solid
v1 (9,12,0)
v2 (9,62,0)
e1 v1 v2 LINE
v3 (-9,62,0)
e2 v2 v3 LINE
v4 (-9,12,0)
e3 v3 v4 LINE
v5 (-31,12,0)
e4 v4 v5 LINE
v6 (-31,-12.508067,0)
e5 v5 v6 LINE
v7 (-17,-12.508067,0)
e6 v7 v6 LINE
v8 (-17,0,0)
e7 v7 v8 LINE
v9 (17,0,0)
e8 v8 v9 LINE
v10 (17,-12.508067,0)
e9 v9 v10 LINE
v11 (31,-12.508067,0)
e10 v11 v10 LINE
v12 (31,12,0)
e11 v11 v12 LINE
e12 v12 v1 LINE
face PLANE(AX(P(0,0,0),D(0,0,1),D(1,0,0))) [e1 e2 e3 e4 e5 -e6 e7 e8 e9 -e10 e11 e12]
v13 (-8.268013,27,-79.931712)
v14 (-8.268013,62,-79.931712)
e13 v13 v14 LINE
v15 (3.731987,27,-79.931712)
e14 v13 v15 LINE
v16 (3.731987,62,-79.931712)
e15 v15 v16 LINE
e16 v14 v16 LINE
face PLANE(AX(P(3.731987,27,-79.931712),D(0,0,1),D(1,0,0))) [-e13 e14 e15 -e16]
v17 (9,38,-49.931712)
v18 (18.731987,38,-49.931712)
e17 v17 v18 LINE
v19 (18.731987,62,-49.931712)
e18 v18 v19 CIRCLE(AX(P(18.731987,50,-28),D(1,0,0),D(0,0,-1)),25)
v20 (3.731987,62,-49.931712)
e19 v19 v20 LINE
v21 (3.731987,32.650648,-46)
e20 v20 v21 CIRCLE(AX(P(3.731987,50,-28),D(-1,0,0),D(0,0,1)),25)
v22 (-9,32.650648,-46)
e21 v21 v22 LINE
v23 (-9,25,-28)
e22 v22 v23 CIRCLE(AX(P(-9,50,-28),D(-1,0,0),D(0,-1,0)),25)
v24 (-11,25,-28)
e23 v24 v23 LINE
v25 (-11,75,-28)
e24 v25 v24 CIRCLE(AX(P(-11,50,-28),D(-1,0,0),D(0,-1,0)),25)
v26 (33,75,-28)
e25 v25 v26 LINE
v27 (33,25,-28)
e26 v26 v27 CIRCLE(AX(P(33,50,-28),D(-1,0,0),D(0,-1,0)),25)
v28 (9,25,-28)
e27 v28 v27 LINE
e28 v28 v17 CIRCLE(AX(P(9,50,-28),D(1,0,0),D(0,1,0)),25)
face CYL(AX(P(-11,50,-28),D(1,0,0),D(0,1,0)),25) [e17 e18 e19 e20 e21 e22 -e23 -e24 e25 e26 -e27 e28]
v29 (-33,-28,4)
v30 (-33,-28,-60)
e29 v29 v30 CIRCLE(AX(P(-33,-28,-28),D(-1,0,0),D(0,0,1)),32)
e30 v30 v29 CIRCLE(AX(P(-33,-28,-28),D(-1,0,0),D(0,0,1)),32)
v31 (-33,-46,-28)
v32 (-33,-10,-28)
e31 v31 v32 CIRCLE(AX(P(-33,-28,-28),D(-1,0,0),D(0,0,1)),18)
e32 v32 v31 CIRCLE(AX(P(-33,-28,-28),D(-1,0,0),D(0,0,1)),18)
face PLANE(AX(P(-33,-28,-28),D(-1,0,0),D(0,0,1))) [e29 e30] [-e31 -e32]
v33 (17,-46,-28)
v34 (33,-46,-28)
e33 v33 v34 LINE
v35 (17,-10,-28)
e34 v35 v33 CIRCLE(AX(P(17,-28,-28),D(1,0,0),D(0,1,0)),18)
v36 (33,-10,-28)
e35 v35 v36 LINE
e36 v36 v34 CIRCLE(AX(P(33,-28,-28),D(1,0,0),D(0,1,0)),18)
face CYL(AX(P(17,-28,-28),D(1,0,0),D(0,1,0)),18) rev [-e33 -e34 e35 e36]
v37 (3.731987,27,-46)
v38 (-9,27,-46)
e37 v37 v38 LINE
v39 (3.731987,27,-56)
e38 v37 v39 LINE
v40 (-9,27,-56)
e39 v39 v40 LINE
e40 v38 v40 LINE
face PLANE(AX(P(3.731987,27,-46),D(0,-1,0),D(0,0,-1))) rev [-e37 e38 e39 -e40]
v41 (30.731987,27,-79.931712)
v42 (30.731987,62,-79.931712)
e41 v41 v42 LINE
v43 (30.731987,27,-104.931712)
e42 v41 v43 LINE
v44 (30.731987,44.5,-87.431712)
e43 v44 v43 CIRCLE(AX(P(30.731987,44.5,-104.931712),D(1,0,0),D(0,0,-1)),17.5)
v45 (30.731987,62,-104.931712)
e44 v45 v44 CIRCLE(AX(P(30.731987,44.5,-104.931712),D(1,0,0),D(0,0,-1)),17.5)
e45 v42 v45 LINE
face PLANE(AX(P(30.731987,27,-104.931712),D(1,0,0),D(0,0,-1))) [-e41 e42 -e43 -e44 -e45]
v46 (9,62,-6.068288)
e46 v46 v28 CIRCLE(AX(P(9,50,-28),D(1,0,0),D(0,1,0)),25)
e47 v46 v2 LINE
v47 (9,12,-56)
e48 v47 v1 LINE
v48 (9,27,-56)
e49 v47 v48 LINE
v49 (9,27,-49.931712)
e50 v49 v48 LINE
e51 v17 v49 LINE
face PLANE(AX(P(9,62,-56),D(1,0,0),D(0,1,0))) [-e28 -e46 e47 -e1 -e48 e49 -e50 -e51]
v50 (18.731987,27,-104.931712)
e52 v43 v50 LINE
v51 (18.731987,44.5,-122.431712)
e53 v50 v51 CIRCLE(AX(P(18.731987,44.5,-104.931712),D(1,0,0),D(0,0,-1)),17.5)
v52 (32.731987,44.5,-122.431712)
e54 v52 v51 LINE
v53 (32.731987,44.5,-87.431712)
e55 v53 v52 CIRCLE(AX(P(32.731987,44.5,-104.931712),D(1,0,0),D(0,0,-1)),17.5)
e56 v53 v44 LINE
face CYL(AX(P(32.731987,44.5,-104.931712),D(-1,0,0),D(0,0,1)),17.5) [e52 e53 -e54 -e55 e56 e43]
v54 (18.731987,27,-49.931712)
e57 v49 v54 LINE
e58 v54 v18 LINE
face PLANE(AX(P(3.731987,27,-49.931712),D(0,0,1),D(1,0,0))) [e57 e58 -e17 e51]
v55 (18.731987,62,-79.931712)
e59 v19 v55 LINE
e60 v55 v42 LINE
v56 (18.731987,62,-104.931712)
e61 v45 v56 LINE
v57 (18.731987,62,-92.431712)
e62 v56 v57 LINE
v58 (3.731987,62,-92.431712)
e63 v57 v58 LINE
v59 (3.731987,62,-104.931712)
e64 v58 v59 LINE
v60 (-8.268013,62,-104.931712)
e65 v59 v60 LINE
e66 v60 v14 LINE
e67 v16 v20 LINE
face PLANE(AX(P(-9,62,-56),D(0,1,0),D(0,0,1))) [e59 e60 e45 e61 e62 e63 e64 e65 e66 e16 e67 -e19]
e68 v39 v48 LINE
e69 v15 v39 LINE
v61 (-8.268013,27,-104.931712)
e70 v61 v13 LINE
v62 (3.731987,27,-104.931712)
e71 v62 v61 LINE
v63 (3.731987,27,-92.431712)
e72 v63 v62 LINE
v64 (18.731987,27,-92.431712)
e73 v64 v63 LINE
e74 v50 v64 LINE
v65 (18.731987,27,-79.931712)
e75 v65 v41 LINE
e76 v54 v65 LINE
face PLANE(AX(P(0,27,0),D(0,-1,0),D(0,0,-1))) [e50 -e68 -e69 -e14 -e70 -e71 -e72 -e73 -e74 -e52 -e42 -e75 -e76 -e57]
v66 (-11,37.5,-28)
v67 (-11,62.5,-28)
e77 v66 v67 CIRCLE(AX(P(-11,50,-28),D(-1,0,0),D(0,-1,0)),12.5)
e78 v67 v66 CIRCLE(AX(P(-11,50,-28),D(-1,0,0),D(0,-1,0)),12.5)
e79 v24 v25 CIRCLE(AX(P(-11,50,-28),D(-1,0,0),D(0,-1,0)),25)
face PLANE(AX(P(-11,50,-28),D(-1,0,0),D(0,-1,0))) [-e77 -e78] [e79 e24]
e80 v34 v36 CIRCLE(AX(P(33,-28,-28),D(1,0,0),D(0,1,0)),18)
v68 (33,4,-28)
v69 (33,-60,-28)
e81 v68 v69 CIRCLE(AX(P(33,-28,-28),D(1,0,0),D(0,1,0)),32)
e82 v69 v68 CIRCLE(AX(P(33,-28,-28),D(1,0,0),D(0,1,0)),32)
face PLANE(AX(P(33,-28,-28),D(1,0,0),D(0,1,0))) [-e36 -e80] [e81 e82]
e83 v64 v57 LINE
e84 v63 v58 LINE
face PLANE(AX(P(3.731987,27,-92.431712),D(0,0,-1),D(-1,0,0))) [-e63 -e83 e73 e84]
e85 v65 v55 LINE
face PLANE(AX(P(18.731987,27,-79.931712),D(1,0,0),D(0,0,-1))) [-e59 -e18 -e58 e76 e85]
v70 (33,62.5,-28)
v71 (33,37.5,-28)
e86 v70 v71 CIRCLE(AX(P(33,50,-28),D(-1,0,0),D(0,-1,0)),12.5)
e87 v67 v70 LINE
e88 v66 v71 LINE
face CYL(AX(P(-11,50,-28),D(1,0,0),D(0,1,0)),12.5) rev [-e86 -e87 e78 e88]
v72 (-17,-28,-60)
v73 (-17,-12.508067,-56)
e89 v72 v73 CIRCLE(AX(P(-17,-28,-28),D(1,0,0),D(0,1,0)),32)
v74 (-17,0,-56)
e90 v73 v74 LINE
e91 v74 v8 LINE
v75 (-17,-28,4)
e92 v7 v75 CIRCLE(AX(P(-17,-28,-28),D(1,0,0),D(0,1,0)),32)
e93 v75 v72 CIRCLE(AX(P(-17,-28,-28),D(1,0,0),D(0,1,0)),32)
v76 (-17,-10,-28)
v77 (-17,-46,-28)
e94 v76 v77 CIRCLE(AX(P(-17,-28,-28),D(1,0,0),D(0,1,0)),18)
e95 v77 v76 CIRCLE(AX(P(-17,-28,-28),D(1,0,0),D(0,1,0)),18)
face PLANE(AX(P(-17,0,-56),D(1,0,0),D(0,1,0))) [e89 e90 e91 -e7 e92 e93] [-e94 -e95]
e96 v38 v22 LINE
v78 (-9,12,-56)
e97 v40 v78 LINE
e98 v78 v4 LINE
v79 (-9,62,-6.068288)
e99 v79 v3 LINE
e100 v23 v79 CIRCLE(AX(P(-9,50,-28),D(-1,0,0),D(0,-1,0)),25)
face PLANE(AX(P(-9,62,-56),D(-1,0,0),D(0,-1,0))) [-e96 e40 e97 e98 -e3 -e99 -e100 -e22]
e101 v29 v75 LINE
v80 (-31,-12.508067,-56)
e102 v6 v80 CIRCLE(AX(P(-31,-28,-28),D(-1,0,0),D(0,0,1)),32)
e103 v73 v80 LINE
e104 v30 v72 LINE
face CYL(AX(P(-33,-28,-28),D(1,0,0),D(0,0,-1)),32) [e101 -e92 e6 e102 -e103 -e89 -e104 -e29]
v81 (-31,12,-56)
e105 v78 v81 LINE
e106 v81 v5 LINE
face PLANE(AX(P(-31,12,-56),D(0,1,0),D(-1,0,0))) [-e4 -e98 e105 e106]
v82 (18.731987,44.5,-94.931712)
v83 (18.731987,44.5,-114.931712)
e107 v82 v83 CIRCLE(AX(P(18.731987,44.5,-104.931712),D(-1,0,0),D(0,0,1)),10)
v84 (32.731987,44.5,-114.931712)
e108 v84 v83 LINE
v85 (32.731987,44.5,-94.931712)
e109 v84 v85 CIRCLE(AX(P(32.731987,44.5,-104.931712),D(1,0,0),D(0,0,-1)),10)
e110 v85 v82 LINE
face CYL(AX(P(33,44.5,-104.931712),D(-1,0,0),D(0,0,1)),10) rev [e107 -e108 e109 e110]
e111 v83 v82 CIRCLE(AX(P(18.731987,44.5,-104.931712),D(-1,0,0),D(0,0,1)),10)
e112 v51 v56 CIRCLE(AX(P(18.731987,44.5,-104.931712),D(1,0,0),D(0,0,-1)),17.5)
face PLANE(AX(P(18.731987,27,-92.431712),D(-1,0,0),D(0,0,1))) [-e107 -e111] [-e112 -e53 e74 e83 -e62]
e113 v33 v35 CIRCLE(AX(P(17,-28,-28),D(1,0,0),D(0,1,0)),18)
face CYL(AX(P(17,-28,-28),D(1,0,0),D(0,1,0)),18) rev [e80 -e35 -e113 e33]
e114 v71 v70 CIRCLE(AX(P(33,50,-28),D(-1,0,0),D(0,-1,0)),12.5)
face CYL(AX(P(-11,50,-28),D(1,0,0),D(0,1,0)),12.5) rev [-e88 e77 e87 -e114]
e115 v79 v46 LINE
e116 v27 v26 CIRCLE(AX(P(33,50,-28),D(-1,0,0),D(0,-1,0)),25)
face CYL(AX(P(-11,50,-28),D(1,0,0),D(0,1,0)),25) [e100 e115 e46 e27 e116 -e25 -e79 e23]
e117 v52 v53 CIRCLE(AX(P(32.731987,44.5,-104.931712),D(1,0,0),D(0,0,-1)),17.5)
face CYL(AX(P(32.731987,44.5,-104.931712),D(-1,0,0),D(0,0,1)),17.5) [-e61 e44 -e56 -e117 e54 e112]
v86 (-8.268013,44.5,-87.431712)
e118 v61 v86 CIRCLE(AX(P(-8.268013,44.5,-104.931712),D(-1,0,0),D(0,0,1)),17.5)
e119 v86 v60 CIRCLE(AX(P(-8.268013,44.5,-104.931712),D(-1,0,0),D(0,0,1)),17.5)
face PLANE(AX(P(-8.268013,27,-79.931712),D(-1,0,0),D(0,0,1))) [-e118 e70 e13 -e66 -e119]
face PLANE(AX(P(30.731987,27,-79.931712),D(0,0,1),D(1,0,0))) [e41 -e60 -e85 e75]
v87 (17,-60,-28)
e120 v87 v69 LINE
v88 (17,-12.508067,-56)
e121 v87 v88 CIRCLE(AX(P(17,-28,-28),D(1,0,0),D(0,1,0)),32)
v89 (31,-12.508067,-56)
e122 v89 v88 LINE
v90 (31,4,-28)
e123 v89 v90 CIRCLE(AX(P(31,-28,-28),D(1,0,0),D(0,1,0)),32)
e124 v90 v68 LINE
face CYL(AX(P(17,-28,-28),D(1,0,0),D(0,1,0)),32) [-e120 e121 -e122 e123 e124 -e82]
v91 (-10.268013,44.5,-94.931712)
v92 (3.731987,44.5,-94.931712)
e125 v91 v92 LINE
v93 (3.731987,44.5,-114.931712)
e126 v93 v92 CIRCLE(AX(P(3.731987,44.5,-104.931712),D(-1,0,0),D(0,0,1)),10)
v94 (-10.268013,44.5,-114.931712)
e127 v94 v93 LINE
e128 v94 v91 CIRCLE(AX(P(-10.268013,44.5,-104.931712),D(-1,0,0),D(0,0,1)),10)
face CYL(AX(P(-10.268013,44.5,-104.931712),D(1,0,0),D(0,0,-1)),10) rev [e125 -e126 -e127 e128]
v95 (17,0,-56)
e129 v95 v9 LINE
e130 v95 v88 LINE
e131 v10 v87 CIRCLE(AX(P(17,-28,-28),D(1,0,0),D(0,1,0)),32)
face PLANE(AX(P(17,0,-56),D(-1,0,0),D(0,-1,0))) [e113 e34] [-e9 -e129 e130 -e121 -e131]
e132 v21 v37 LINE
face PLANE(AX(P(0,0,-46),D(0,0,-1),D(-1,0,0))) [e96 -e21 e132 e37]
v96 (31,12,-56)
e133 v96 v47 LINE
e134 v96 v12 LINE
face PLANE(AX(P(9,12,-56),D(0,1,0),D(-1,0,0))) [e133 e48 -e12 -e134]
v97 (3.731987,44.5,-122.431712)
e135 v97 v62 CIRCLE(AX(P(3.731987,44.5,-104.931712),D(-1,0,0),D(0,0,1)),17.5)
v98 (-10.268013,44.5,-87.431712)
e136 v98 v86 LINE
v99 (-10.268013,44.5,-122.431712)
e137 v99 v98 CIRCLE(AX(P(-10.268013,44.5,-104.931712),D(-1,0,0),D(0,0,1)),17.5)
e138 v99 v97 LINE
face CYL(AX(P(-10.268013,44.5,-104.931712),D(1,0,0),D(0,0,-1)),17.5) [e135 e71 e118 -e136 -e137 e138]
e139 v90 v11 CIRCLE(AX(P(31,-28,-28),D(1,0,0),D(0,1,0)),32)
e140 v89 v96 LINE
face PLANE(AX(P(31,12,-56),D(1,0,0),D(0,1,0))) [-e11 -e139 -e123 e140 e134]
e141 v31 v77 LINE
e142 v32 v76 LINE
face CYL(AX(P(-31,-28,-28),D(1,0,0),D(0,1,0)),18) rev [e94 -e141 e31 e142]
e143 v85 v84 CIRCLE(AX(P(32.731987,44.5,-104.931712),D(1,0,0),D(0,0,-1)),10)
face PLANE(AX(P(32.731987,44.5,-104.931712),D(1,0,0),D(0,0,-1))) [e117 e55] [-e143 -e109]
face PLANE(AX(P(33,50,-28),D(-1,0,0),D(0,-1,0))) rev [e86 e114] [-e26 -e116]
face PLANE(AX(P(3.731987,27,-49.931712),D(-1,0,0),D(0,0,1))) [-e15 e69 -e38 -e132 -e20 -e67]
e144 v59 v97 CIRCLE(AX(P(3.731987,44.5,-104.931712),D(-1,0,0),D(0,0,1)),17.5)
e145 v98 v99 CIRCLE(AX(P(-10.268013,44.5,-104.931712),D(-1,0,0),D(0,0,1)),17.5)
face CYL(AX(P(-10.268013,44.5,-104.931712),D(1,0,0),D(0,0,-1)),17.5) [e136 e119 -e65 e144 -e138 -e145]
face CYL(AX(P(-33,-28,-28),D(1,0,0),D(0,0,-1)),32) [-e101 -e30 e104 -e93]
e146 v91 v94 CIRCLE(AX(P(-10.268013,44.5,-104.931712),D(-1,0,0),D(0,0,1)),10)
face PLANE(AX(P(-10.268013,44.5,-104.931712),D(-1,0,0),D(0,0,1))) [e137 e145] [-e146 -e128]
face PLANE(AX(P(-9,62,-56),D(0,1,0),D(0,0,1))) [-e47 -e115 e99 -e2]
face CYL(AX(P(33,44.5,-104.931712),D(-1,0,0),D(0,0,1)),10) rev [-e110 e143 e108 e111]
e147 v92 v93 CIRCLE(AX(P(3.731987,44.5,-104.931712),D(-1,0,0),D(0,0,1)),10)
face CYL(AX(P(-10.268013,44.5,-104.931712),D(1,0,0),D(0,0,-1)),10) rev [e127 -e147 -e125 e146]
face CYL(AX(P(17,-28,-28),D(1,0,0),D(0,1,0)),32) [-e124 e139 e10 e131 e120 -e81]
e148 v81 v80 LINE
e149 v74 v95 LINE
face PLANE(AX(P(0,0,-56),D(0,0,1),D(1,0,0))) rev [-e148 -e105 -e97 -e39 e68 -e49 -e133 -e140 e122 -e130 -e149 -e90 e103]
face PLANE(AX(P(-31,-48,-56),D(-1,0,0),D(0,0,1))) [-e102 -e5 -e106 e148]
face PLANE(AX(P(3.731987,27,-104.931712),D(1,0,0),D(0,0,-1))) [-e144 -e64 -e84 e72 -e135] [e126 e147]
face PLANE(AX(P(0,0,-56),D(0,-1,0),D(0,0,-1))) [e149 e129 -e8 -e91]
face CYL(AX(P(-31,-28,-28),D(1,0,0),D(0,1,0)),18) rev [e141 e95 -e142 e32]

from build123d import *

# Parameters (mm, degrees)
BRACKET_BODY_DEPTH      = 56
SLOT_SKETCH_W           = 62
SLOT_SKETCH_H           = 20
SLOT_CUT_DEPTH          = 90.112288715
LUG_A_SKETCH_R          = 32
LUG_A_SKETCH_R_2        = 18
LUG_A_14MM_DEPTH        = 14
SPACER_START            = 2
SPACER_A_SKETCH_R       = 32
SPACER_A_SKETCH_R_2     = 18
SPACER_A_2MM_DEPTH      = 2
HOLE_A_SKETCH_R         = 18
HOLE_A_DEPTH            = 107.244999882
SPACER_B_SKETCH_R       = 32
SPACER_B_SKETCH_R_2     = 18
SPACER_B_2MM_DEPTH      = 2
LUG_B_SKETCH_R          = 32
LUG_B_SKETCH_R_2        = 18
LUG_B_14MM_DEPTH        = 14
PAD_SKETCH_R            = 25
PAD_SKETCH_R_2          = 12.5
PAD_2MM_DEPTH           = 2
HUB_START               = -44
HUB_SKETCH_R            = 25
HUB_SKETCH_R_2          = 12.5
HUB_44MM_DEPTH          = 44
HUB_BORE_SKETCH_R       = 12.5
HUB_BORE_DEPTH          = 44
ARM_35MM_DEPTH          = 35
ARM_SPACER_A_SKETCH_R   = 17.5
ARM_SPACER_A_SKETCH_R_2 = 10
ARM_SPACER_A_2MM_DEPTH  = 2
ARM_START               = -12
ARM_LUG_SKETCH_R        = 17.5
ARM_LUG_SKETCH_R_2      = 10
ARM_LUG_12MM_DEPTH      = 12
ARM_HOLE_SKETCH_R       = 10
ARM_HOLE_DEPTH          = 150.390672563
ARM_SPACER_B_SKETCH_R   = 17.5
ARM_SPACER_B_SKETCH_R_2 = 10
ARM_SPACER_B_2MM_DEPTH  = 2
ARM_START_2             = -14
ARM_EYE_SKETCH_R        = 17.5
ARM_EYE_SKETCH_R_2      = 10
ARM_EYE_14MM_DEPTH      = 14
ARM_SLOT_SKETCH_W       = 12.731987003
ARM_SLOT_SKETCH_H       = 35
ARM_SLOT_10MM_DEPTH     = 10
PIN_START               = -16
PIN_BOSS_SKETCH_R       = 25
PIN_BOSS_16MM_DEPTH     = 16
PIN_BOSS_HOLE_SKETCH_R  = 12.5
PIN_BOSS_HOLE_DEPTH     = 151.168319402


with BuildPart() as part:
    # Bracket Profile Sketch → Bracket Body (new body)
    with BuildSketch(Plane.XY):
        Polygon((0, 0), (17, 0), (17, -48), (31, -48), (31, 12), (9, 12), (9, 62), (-9, 62), (-9, 12), (-31, 12), (-31, -48), (-17, -48), (-17, 0), align=None)
    extrude(amount=-BRACKET_BODY_DEPTH)

    # Slot Sketch → Slot Cut (cut, through all)
    with BuildSketch(Plane.XY):
        with Locations((0, -38)):
            Rectangle(SLOT_SKETCH_W, SLOT_SKETCH_H)
    extrude(amount=-SLOT_CUT_DEPTH, mode=Mode.SUBTRACT)

    # Lug A Sketch → Lug A 14mm (add)
    with BuildSketch(Plane(origin=(31, 0, 0), x_dir=(0, 0, -1), z_dir=(1, 0, 0))):
        with Locations((28, -28)):
            Circle(LUG_A_SKETCH_R)
        with Locations((28, -28)):
            Circle(LUG_A_SKETCH_R_2, mode=Mode.SUBTRACT)
    extrude(amount=-LUG_A_14MM_DEPTH)

    # Spacer A Sketch → Spacer A 2mm (add)
    with BuildSketch(Plane(origin=(31, 0, 0), x_dir=(0, 0, -1), z_dir=(1, 0, 0)).offset(SPACER_START)):
        with Locations(Location((28, -28, 0), (0, 0, 90))):
            Circle(SPACER_A_SKETCH_R)
        with Locations(Location((28, -28, 0), (0, 0, 90))):
            Circle(SPACER_A_SKETCH_R_2, mode=Mode.SUBTRACT)
    extrude(amount=-SPACER_A_2MM_DEPTH)

    # Hole A Sketch → Hole A (cut, through all)
    with BuildSketch(Plane(origin=(31, 0, 0), x_dir=(0, 0, -1), z_dir=(1, 0, 0))):
        with Locations(Location((28, -28, 0), (0, 0, 90))):
            Circle(HOLE_A_SKETCH_R)
    extrude(amount=-HOLE_A_DEPTH, mode=Mode.SUBTRACT)

    # Spacer B Sketch → Spacer B 2mm (add)
    with BuildSketch(Plane.ZY.offset(31)):
        with Locations(Location((-28, -28, 0), (0, 0, 90))):
            Circle(SPACER_B_SKETCH_R)
        with Locations(Location((-28, -28, 0), (0, 0, 90))):
            Circle(SPACER_B_SKETCH_R_2, mode=Mode.SUBTRACT)
    extrude(amount=SPACER_B_2MM_DEPTH)

    # Lug B Sketch → Lug B 14mm (add)
    with BuildSketch(Plane(origin=(-17, 0, 0), x_dir=(0, 0, -1), z_dir=(1, 0, 0))):
        with Locations(Location((28, -28, 0), (0, 0, 90))):
            Circle(LUG_B_SKETCH_R)
        with Locations(Location((28, -28, 0), (0, 0, 90))):
            Circle(LUG_B_SKETCH_R_2, mode=Mode.SUBTRACT)
    extrude(amount=-LUG_B_14MM_DEPTH)

    # Pad Sketch → Pad 2mm (add)
    with BuildSketch(Plane.ZY.offset(9)):
        with Locations(Location((-28, 50, 0), (0, 0, 151.314597986))):
            Circle(PAD_SKETCH_R)
        with Locations(Location((-28, 50, 0), (0, 0, 73.739795292))):
            Circle(PAD_SKETCH_R_2, mode=Mode.SUBTRACT)
    extrude(amount=PAD_2MM_DEPTH)

    # Hub Sketch → Hub 44mm (add)
    with BuildSketch(Plane.ZY.offset(11).offset(HUB_START)):
        with Locations(Location((-28, 50, 0), (0, 0, 270))):
            Circle(HUB_SKETCH_R)
        with Locations(Location((-28, 50, 0), (0, 0, 270))):
            Circle(HUB_SKETCH_R_2, mode=Mode.SUBTRACT)
    extrude(amount=HUB_44MM_DEPTH)

    # Hub Bore Sketch → Hub Bore (cut)
    with BuildSketch(Plane.ZY.offset(9).offset(HUB_START)):
        with Locations(Location((-28, 50, 0), (0, 0, 270))):
            Circle(HUB_BORE_SKETCH_R)
    extrude(amount=HUB_BORE_DEPTH, mode=Mode.SUBTRACT)

    # Arm Profile Sketch → Arm 35mm (add)
    with BuildSketch(Plane(origin=(0, 62, 0), x_dir=(1, 0, 0), z_dir=(0, 1, 0))):
        Polygon((3.731987003, 49.931712199), (3.731987003, 79.931712199), (-8.268012997, 79.931712199), (-8.268012997, 104.931712199), (3.731987003, 104.931712199), (3.731987003, 92.431712199), (18.731987003, 92.431712199), (18.731987003, 104.931712199), (30.731987003, 104.931712199), (30.731987003, 79.931712199), (18.731987003, 79.931712199), (18.731987003, 49.931712199), align=None)
    extrude(amount=-ARM_35MM_DEPTH)

    # Arm Spacer A Sketch → Arm Spacer A 2mm (add)
    with BuildSketch(Plane.ZY.offset(8.268012997)):
        with Locations(Location((-104.931712199, 44.5, 0), (0, 0, 270))):
            Circle(ARM_SPACER_A_SKETCH_R)
        with Locations(Location((-104.931712199, 44.5, 0), (0, 0, 90))):
            Circle(ARM_SPACER_A_SKETCH_R_2, mode=Mode.SUBTRACT)
    extrude(amount=ARM_SPACER_A_2MM_DEPTH)

    # Arm Lug Sketch → Arm Lug 12mm (add)
    with BuildSketch(Plane.ZY.offset(8.268012997).offset(ARM_START)):
        with Locations(Location((-104.931712199, 44.5, 0), (0, 0, 90))):
            Circle(ARM_LUG_SKETCH_R)
        with Locations(Location((-104.931712199, 44.5, 0), (0, 0, 90))):
            Circle(ARM_LUG_SKETCH_R_2, mode=Mode.SUBTRACT)
    extrude(amount=ARM_LUG_12MM_DEPTH)

    # Arm Hole Sketch → Arm Hole (cut, through all)
    with BuildSketch(Plane.ZY.offset(8.268012997)):
        with Locations((-104.931712199, 44.5)):
            Circle(ARM_HOLE_SKETCH_R)
    extrude(amount=-ARM_HOLE_DEPTH, mode=Mode.SUBTRACT)

    # Arm Spacer B Sketch → Arm Spacer B 2mm (add)
    with BuildSketch(Plane(origin=(30.731987003, 0, 0), x_dir=(0, 0, -1), z_dir=(1, 0, 0))):
        with Locations(Location((104.931712199, 44.5, 0), (0, 0, 90))):
            Circle(ARM_SPACER_B_SKETCH_R)
        with Locations(Location((104.931712199, 44.5, 0), (0, 0, 180))):
            Circle(ARM_SPACER_B_SKETCH_R_2, mode=Mode.SUBTRACT)
    extrude(amount=ARM_SPACER_B_2MM_DEPTH)

    # Arm Eye Sketch → Arm Eye 14mm (add)
    with BuildSketch(Plane(origin=(32.731987003, 0, 0), x_dir=(0, 0, -1), z_dir=(1, 0, 0)).offset(ARM_START_2)):
        with Locations(Location((104.931712199, 44.5, 0), (0, 0, 90))):
            Circle(ARM_EYE_SKETCH_R)
        with Locations(Location((104.931712199, 44.5, 0), (0, 0, 180))):
            Circle(ARM_EYE_SKETCH_R_2, mode=Mode.SUBTRACT)
    extrude(amount=ARM_EYE_14MM_DEPTH)

    # Arm Slot Sketch → Arm Slot 10mm (cut)
    with BuildSketch(Plane(origin=(0, 0, -56), x_dir=(-1, 0, 0), z_dir=(0, 0, -1))):
        with Locations((2.634006498, 44.5)):
            Rectangle(ARM_SLOT_SKETCH_W, ARM_SLOT_SKETCH_H)
    extrude(amount=-ARM_SLOT_10MM_DEPTH, mode=Mode.SUBTRACT)

    # Pin Boss Sketch → Pin Boss 16mm (add)
    with BuildSketch(Plane.ZY.offset(11).offset(PIN_START)):
        with Locations(Location((-28, 50, 0), (0, 0, 270))):
            Circle(PIN_BOSS_SKETCH_R)
    extrude(amount=PIN_BOSS_16MM_DEPTH)

    # Pin Boss Hole Sketch → Pin Boss Hole (cut, through all)
    with BuildSketch(Plane.ZY.offset(11)):
        with Locations(Location((-28, 50, 0), (0, 0, 270))):
            Circle(PIN_BOSS_HOLE_SKETCH_R)
    extrude(amount=-PIN_BOSS_HOLE_DEPTH, mode=Mode.SUBTRACT)


solid = part.part
